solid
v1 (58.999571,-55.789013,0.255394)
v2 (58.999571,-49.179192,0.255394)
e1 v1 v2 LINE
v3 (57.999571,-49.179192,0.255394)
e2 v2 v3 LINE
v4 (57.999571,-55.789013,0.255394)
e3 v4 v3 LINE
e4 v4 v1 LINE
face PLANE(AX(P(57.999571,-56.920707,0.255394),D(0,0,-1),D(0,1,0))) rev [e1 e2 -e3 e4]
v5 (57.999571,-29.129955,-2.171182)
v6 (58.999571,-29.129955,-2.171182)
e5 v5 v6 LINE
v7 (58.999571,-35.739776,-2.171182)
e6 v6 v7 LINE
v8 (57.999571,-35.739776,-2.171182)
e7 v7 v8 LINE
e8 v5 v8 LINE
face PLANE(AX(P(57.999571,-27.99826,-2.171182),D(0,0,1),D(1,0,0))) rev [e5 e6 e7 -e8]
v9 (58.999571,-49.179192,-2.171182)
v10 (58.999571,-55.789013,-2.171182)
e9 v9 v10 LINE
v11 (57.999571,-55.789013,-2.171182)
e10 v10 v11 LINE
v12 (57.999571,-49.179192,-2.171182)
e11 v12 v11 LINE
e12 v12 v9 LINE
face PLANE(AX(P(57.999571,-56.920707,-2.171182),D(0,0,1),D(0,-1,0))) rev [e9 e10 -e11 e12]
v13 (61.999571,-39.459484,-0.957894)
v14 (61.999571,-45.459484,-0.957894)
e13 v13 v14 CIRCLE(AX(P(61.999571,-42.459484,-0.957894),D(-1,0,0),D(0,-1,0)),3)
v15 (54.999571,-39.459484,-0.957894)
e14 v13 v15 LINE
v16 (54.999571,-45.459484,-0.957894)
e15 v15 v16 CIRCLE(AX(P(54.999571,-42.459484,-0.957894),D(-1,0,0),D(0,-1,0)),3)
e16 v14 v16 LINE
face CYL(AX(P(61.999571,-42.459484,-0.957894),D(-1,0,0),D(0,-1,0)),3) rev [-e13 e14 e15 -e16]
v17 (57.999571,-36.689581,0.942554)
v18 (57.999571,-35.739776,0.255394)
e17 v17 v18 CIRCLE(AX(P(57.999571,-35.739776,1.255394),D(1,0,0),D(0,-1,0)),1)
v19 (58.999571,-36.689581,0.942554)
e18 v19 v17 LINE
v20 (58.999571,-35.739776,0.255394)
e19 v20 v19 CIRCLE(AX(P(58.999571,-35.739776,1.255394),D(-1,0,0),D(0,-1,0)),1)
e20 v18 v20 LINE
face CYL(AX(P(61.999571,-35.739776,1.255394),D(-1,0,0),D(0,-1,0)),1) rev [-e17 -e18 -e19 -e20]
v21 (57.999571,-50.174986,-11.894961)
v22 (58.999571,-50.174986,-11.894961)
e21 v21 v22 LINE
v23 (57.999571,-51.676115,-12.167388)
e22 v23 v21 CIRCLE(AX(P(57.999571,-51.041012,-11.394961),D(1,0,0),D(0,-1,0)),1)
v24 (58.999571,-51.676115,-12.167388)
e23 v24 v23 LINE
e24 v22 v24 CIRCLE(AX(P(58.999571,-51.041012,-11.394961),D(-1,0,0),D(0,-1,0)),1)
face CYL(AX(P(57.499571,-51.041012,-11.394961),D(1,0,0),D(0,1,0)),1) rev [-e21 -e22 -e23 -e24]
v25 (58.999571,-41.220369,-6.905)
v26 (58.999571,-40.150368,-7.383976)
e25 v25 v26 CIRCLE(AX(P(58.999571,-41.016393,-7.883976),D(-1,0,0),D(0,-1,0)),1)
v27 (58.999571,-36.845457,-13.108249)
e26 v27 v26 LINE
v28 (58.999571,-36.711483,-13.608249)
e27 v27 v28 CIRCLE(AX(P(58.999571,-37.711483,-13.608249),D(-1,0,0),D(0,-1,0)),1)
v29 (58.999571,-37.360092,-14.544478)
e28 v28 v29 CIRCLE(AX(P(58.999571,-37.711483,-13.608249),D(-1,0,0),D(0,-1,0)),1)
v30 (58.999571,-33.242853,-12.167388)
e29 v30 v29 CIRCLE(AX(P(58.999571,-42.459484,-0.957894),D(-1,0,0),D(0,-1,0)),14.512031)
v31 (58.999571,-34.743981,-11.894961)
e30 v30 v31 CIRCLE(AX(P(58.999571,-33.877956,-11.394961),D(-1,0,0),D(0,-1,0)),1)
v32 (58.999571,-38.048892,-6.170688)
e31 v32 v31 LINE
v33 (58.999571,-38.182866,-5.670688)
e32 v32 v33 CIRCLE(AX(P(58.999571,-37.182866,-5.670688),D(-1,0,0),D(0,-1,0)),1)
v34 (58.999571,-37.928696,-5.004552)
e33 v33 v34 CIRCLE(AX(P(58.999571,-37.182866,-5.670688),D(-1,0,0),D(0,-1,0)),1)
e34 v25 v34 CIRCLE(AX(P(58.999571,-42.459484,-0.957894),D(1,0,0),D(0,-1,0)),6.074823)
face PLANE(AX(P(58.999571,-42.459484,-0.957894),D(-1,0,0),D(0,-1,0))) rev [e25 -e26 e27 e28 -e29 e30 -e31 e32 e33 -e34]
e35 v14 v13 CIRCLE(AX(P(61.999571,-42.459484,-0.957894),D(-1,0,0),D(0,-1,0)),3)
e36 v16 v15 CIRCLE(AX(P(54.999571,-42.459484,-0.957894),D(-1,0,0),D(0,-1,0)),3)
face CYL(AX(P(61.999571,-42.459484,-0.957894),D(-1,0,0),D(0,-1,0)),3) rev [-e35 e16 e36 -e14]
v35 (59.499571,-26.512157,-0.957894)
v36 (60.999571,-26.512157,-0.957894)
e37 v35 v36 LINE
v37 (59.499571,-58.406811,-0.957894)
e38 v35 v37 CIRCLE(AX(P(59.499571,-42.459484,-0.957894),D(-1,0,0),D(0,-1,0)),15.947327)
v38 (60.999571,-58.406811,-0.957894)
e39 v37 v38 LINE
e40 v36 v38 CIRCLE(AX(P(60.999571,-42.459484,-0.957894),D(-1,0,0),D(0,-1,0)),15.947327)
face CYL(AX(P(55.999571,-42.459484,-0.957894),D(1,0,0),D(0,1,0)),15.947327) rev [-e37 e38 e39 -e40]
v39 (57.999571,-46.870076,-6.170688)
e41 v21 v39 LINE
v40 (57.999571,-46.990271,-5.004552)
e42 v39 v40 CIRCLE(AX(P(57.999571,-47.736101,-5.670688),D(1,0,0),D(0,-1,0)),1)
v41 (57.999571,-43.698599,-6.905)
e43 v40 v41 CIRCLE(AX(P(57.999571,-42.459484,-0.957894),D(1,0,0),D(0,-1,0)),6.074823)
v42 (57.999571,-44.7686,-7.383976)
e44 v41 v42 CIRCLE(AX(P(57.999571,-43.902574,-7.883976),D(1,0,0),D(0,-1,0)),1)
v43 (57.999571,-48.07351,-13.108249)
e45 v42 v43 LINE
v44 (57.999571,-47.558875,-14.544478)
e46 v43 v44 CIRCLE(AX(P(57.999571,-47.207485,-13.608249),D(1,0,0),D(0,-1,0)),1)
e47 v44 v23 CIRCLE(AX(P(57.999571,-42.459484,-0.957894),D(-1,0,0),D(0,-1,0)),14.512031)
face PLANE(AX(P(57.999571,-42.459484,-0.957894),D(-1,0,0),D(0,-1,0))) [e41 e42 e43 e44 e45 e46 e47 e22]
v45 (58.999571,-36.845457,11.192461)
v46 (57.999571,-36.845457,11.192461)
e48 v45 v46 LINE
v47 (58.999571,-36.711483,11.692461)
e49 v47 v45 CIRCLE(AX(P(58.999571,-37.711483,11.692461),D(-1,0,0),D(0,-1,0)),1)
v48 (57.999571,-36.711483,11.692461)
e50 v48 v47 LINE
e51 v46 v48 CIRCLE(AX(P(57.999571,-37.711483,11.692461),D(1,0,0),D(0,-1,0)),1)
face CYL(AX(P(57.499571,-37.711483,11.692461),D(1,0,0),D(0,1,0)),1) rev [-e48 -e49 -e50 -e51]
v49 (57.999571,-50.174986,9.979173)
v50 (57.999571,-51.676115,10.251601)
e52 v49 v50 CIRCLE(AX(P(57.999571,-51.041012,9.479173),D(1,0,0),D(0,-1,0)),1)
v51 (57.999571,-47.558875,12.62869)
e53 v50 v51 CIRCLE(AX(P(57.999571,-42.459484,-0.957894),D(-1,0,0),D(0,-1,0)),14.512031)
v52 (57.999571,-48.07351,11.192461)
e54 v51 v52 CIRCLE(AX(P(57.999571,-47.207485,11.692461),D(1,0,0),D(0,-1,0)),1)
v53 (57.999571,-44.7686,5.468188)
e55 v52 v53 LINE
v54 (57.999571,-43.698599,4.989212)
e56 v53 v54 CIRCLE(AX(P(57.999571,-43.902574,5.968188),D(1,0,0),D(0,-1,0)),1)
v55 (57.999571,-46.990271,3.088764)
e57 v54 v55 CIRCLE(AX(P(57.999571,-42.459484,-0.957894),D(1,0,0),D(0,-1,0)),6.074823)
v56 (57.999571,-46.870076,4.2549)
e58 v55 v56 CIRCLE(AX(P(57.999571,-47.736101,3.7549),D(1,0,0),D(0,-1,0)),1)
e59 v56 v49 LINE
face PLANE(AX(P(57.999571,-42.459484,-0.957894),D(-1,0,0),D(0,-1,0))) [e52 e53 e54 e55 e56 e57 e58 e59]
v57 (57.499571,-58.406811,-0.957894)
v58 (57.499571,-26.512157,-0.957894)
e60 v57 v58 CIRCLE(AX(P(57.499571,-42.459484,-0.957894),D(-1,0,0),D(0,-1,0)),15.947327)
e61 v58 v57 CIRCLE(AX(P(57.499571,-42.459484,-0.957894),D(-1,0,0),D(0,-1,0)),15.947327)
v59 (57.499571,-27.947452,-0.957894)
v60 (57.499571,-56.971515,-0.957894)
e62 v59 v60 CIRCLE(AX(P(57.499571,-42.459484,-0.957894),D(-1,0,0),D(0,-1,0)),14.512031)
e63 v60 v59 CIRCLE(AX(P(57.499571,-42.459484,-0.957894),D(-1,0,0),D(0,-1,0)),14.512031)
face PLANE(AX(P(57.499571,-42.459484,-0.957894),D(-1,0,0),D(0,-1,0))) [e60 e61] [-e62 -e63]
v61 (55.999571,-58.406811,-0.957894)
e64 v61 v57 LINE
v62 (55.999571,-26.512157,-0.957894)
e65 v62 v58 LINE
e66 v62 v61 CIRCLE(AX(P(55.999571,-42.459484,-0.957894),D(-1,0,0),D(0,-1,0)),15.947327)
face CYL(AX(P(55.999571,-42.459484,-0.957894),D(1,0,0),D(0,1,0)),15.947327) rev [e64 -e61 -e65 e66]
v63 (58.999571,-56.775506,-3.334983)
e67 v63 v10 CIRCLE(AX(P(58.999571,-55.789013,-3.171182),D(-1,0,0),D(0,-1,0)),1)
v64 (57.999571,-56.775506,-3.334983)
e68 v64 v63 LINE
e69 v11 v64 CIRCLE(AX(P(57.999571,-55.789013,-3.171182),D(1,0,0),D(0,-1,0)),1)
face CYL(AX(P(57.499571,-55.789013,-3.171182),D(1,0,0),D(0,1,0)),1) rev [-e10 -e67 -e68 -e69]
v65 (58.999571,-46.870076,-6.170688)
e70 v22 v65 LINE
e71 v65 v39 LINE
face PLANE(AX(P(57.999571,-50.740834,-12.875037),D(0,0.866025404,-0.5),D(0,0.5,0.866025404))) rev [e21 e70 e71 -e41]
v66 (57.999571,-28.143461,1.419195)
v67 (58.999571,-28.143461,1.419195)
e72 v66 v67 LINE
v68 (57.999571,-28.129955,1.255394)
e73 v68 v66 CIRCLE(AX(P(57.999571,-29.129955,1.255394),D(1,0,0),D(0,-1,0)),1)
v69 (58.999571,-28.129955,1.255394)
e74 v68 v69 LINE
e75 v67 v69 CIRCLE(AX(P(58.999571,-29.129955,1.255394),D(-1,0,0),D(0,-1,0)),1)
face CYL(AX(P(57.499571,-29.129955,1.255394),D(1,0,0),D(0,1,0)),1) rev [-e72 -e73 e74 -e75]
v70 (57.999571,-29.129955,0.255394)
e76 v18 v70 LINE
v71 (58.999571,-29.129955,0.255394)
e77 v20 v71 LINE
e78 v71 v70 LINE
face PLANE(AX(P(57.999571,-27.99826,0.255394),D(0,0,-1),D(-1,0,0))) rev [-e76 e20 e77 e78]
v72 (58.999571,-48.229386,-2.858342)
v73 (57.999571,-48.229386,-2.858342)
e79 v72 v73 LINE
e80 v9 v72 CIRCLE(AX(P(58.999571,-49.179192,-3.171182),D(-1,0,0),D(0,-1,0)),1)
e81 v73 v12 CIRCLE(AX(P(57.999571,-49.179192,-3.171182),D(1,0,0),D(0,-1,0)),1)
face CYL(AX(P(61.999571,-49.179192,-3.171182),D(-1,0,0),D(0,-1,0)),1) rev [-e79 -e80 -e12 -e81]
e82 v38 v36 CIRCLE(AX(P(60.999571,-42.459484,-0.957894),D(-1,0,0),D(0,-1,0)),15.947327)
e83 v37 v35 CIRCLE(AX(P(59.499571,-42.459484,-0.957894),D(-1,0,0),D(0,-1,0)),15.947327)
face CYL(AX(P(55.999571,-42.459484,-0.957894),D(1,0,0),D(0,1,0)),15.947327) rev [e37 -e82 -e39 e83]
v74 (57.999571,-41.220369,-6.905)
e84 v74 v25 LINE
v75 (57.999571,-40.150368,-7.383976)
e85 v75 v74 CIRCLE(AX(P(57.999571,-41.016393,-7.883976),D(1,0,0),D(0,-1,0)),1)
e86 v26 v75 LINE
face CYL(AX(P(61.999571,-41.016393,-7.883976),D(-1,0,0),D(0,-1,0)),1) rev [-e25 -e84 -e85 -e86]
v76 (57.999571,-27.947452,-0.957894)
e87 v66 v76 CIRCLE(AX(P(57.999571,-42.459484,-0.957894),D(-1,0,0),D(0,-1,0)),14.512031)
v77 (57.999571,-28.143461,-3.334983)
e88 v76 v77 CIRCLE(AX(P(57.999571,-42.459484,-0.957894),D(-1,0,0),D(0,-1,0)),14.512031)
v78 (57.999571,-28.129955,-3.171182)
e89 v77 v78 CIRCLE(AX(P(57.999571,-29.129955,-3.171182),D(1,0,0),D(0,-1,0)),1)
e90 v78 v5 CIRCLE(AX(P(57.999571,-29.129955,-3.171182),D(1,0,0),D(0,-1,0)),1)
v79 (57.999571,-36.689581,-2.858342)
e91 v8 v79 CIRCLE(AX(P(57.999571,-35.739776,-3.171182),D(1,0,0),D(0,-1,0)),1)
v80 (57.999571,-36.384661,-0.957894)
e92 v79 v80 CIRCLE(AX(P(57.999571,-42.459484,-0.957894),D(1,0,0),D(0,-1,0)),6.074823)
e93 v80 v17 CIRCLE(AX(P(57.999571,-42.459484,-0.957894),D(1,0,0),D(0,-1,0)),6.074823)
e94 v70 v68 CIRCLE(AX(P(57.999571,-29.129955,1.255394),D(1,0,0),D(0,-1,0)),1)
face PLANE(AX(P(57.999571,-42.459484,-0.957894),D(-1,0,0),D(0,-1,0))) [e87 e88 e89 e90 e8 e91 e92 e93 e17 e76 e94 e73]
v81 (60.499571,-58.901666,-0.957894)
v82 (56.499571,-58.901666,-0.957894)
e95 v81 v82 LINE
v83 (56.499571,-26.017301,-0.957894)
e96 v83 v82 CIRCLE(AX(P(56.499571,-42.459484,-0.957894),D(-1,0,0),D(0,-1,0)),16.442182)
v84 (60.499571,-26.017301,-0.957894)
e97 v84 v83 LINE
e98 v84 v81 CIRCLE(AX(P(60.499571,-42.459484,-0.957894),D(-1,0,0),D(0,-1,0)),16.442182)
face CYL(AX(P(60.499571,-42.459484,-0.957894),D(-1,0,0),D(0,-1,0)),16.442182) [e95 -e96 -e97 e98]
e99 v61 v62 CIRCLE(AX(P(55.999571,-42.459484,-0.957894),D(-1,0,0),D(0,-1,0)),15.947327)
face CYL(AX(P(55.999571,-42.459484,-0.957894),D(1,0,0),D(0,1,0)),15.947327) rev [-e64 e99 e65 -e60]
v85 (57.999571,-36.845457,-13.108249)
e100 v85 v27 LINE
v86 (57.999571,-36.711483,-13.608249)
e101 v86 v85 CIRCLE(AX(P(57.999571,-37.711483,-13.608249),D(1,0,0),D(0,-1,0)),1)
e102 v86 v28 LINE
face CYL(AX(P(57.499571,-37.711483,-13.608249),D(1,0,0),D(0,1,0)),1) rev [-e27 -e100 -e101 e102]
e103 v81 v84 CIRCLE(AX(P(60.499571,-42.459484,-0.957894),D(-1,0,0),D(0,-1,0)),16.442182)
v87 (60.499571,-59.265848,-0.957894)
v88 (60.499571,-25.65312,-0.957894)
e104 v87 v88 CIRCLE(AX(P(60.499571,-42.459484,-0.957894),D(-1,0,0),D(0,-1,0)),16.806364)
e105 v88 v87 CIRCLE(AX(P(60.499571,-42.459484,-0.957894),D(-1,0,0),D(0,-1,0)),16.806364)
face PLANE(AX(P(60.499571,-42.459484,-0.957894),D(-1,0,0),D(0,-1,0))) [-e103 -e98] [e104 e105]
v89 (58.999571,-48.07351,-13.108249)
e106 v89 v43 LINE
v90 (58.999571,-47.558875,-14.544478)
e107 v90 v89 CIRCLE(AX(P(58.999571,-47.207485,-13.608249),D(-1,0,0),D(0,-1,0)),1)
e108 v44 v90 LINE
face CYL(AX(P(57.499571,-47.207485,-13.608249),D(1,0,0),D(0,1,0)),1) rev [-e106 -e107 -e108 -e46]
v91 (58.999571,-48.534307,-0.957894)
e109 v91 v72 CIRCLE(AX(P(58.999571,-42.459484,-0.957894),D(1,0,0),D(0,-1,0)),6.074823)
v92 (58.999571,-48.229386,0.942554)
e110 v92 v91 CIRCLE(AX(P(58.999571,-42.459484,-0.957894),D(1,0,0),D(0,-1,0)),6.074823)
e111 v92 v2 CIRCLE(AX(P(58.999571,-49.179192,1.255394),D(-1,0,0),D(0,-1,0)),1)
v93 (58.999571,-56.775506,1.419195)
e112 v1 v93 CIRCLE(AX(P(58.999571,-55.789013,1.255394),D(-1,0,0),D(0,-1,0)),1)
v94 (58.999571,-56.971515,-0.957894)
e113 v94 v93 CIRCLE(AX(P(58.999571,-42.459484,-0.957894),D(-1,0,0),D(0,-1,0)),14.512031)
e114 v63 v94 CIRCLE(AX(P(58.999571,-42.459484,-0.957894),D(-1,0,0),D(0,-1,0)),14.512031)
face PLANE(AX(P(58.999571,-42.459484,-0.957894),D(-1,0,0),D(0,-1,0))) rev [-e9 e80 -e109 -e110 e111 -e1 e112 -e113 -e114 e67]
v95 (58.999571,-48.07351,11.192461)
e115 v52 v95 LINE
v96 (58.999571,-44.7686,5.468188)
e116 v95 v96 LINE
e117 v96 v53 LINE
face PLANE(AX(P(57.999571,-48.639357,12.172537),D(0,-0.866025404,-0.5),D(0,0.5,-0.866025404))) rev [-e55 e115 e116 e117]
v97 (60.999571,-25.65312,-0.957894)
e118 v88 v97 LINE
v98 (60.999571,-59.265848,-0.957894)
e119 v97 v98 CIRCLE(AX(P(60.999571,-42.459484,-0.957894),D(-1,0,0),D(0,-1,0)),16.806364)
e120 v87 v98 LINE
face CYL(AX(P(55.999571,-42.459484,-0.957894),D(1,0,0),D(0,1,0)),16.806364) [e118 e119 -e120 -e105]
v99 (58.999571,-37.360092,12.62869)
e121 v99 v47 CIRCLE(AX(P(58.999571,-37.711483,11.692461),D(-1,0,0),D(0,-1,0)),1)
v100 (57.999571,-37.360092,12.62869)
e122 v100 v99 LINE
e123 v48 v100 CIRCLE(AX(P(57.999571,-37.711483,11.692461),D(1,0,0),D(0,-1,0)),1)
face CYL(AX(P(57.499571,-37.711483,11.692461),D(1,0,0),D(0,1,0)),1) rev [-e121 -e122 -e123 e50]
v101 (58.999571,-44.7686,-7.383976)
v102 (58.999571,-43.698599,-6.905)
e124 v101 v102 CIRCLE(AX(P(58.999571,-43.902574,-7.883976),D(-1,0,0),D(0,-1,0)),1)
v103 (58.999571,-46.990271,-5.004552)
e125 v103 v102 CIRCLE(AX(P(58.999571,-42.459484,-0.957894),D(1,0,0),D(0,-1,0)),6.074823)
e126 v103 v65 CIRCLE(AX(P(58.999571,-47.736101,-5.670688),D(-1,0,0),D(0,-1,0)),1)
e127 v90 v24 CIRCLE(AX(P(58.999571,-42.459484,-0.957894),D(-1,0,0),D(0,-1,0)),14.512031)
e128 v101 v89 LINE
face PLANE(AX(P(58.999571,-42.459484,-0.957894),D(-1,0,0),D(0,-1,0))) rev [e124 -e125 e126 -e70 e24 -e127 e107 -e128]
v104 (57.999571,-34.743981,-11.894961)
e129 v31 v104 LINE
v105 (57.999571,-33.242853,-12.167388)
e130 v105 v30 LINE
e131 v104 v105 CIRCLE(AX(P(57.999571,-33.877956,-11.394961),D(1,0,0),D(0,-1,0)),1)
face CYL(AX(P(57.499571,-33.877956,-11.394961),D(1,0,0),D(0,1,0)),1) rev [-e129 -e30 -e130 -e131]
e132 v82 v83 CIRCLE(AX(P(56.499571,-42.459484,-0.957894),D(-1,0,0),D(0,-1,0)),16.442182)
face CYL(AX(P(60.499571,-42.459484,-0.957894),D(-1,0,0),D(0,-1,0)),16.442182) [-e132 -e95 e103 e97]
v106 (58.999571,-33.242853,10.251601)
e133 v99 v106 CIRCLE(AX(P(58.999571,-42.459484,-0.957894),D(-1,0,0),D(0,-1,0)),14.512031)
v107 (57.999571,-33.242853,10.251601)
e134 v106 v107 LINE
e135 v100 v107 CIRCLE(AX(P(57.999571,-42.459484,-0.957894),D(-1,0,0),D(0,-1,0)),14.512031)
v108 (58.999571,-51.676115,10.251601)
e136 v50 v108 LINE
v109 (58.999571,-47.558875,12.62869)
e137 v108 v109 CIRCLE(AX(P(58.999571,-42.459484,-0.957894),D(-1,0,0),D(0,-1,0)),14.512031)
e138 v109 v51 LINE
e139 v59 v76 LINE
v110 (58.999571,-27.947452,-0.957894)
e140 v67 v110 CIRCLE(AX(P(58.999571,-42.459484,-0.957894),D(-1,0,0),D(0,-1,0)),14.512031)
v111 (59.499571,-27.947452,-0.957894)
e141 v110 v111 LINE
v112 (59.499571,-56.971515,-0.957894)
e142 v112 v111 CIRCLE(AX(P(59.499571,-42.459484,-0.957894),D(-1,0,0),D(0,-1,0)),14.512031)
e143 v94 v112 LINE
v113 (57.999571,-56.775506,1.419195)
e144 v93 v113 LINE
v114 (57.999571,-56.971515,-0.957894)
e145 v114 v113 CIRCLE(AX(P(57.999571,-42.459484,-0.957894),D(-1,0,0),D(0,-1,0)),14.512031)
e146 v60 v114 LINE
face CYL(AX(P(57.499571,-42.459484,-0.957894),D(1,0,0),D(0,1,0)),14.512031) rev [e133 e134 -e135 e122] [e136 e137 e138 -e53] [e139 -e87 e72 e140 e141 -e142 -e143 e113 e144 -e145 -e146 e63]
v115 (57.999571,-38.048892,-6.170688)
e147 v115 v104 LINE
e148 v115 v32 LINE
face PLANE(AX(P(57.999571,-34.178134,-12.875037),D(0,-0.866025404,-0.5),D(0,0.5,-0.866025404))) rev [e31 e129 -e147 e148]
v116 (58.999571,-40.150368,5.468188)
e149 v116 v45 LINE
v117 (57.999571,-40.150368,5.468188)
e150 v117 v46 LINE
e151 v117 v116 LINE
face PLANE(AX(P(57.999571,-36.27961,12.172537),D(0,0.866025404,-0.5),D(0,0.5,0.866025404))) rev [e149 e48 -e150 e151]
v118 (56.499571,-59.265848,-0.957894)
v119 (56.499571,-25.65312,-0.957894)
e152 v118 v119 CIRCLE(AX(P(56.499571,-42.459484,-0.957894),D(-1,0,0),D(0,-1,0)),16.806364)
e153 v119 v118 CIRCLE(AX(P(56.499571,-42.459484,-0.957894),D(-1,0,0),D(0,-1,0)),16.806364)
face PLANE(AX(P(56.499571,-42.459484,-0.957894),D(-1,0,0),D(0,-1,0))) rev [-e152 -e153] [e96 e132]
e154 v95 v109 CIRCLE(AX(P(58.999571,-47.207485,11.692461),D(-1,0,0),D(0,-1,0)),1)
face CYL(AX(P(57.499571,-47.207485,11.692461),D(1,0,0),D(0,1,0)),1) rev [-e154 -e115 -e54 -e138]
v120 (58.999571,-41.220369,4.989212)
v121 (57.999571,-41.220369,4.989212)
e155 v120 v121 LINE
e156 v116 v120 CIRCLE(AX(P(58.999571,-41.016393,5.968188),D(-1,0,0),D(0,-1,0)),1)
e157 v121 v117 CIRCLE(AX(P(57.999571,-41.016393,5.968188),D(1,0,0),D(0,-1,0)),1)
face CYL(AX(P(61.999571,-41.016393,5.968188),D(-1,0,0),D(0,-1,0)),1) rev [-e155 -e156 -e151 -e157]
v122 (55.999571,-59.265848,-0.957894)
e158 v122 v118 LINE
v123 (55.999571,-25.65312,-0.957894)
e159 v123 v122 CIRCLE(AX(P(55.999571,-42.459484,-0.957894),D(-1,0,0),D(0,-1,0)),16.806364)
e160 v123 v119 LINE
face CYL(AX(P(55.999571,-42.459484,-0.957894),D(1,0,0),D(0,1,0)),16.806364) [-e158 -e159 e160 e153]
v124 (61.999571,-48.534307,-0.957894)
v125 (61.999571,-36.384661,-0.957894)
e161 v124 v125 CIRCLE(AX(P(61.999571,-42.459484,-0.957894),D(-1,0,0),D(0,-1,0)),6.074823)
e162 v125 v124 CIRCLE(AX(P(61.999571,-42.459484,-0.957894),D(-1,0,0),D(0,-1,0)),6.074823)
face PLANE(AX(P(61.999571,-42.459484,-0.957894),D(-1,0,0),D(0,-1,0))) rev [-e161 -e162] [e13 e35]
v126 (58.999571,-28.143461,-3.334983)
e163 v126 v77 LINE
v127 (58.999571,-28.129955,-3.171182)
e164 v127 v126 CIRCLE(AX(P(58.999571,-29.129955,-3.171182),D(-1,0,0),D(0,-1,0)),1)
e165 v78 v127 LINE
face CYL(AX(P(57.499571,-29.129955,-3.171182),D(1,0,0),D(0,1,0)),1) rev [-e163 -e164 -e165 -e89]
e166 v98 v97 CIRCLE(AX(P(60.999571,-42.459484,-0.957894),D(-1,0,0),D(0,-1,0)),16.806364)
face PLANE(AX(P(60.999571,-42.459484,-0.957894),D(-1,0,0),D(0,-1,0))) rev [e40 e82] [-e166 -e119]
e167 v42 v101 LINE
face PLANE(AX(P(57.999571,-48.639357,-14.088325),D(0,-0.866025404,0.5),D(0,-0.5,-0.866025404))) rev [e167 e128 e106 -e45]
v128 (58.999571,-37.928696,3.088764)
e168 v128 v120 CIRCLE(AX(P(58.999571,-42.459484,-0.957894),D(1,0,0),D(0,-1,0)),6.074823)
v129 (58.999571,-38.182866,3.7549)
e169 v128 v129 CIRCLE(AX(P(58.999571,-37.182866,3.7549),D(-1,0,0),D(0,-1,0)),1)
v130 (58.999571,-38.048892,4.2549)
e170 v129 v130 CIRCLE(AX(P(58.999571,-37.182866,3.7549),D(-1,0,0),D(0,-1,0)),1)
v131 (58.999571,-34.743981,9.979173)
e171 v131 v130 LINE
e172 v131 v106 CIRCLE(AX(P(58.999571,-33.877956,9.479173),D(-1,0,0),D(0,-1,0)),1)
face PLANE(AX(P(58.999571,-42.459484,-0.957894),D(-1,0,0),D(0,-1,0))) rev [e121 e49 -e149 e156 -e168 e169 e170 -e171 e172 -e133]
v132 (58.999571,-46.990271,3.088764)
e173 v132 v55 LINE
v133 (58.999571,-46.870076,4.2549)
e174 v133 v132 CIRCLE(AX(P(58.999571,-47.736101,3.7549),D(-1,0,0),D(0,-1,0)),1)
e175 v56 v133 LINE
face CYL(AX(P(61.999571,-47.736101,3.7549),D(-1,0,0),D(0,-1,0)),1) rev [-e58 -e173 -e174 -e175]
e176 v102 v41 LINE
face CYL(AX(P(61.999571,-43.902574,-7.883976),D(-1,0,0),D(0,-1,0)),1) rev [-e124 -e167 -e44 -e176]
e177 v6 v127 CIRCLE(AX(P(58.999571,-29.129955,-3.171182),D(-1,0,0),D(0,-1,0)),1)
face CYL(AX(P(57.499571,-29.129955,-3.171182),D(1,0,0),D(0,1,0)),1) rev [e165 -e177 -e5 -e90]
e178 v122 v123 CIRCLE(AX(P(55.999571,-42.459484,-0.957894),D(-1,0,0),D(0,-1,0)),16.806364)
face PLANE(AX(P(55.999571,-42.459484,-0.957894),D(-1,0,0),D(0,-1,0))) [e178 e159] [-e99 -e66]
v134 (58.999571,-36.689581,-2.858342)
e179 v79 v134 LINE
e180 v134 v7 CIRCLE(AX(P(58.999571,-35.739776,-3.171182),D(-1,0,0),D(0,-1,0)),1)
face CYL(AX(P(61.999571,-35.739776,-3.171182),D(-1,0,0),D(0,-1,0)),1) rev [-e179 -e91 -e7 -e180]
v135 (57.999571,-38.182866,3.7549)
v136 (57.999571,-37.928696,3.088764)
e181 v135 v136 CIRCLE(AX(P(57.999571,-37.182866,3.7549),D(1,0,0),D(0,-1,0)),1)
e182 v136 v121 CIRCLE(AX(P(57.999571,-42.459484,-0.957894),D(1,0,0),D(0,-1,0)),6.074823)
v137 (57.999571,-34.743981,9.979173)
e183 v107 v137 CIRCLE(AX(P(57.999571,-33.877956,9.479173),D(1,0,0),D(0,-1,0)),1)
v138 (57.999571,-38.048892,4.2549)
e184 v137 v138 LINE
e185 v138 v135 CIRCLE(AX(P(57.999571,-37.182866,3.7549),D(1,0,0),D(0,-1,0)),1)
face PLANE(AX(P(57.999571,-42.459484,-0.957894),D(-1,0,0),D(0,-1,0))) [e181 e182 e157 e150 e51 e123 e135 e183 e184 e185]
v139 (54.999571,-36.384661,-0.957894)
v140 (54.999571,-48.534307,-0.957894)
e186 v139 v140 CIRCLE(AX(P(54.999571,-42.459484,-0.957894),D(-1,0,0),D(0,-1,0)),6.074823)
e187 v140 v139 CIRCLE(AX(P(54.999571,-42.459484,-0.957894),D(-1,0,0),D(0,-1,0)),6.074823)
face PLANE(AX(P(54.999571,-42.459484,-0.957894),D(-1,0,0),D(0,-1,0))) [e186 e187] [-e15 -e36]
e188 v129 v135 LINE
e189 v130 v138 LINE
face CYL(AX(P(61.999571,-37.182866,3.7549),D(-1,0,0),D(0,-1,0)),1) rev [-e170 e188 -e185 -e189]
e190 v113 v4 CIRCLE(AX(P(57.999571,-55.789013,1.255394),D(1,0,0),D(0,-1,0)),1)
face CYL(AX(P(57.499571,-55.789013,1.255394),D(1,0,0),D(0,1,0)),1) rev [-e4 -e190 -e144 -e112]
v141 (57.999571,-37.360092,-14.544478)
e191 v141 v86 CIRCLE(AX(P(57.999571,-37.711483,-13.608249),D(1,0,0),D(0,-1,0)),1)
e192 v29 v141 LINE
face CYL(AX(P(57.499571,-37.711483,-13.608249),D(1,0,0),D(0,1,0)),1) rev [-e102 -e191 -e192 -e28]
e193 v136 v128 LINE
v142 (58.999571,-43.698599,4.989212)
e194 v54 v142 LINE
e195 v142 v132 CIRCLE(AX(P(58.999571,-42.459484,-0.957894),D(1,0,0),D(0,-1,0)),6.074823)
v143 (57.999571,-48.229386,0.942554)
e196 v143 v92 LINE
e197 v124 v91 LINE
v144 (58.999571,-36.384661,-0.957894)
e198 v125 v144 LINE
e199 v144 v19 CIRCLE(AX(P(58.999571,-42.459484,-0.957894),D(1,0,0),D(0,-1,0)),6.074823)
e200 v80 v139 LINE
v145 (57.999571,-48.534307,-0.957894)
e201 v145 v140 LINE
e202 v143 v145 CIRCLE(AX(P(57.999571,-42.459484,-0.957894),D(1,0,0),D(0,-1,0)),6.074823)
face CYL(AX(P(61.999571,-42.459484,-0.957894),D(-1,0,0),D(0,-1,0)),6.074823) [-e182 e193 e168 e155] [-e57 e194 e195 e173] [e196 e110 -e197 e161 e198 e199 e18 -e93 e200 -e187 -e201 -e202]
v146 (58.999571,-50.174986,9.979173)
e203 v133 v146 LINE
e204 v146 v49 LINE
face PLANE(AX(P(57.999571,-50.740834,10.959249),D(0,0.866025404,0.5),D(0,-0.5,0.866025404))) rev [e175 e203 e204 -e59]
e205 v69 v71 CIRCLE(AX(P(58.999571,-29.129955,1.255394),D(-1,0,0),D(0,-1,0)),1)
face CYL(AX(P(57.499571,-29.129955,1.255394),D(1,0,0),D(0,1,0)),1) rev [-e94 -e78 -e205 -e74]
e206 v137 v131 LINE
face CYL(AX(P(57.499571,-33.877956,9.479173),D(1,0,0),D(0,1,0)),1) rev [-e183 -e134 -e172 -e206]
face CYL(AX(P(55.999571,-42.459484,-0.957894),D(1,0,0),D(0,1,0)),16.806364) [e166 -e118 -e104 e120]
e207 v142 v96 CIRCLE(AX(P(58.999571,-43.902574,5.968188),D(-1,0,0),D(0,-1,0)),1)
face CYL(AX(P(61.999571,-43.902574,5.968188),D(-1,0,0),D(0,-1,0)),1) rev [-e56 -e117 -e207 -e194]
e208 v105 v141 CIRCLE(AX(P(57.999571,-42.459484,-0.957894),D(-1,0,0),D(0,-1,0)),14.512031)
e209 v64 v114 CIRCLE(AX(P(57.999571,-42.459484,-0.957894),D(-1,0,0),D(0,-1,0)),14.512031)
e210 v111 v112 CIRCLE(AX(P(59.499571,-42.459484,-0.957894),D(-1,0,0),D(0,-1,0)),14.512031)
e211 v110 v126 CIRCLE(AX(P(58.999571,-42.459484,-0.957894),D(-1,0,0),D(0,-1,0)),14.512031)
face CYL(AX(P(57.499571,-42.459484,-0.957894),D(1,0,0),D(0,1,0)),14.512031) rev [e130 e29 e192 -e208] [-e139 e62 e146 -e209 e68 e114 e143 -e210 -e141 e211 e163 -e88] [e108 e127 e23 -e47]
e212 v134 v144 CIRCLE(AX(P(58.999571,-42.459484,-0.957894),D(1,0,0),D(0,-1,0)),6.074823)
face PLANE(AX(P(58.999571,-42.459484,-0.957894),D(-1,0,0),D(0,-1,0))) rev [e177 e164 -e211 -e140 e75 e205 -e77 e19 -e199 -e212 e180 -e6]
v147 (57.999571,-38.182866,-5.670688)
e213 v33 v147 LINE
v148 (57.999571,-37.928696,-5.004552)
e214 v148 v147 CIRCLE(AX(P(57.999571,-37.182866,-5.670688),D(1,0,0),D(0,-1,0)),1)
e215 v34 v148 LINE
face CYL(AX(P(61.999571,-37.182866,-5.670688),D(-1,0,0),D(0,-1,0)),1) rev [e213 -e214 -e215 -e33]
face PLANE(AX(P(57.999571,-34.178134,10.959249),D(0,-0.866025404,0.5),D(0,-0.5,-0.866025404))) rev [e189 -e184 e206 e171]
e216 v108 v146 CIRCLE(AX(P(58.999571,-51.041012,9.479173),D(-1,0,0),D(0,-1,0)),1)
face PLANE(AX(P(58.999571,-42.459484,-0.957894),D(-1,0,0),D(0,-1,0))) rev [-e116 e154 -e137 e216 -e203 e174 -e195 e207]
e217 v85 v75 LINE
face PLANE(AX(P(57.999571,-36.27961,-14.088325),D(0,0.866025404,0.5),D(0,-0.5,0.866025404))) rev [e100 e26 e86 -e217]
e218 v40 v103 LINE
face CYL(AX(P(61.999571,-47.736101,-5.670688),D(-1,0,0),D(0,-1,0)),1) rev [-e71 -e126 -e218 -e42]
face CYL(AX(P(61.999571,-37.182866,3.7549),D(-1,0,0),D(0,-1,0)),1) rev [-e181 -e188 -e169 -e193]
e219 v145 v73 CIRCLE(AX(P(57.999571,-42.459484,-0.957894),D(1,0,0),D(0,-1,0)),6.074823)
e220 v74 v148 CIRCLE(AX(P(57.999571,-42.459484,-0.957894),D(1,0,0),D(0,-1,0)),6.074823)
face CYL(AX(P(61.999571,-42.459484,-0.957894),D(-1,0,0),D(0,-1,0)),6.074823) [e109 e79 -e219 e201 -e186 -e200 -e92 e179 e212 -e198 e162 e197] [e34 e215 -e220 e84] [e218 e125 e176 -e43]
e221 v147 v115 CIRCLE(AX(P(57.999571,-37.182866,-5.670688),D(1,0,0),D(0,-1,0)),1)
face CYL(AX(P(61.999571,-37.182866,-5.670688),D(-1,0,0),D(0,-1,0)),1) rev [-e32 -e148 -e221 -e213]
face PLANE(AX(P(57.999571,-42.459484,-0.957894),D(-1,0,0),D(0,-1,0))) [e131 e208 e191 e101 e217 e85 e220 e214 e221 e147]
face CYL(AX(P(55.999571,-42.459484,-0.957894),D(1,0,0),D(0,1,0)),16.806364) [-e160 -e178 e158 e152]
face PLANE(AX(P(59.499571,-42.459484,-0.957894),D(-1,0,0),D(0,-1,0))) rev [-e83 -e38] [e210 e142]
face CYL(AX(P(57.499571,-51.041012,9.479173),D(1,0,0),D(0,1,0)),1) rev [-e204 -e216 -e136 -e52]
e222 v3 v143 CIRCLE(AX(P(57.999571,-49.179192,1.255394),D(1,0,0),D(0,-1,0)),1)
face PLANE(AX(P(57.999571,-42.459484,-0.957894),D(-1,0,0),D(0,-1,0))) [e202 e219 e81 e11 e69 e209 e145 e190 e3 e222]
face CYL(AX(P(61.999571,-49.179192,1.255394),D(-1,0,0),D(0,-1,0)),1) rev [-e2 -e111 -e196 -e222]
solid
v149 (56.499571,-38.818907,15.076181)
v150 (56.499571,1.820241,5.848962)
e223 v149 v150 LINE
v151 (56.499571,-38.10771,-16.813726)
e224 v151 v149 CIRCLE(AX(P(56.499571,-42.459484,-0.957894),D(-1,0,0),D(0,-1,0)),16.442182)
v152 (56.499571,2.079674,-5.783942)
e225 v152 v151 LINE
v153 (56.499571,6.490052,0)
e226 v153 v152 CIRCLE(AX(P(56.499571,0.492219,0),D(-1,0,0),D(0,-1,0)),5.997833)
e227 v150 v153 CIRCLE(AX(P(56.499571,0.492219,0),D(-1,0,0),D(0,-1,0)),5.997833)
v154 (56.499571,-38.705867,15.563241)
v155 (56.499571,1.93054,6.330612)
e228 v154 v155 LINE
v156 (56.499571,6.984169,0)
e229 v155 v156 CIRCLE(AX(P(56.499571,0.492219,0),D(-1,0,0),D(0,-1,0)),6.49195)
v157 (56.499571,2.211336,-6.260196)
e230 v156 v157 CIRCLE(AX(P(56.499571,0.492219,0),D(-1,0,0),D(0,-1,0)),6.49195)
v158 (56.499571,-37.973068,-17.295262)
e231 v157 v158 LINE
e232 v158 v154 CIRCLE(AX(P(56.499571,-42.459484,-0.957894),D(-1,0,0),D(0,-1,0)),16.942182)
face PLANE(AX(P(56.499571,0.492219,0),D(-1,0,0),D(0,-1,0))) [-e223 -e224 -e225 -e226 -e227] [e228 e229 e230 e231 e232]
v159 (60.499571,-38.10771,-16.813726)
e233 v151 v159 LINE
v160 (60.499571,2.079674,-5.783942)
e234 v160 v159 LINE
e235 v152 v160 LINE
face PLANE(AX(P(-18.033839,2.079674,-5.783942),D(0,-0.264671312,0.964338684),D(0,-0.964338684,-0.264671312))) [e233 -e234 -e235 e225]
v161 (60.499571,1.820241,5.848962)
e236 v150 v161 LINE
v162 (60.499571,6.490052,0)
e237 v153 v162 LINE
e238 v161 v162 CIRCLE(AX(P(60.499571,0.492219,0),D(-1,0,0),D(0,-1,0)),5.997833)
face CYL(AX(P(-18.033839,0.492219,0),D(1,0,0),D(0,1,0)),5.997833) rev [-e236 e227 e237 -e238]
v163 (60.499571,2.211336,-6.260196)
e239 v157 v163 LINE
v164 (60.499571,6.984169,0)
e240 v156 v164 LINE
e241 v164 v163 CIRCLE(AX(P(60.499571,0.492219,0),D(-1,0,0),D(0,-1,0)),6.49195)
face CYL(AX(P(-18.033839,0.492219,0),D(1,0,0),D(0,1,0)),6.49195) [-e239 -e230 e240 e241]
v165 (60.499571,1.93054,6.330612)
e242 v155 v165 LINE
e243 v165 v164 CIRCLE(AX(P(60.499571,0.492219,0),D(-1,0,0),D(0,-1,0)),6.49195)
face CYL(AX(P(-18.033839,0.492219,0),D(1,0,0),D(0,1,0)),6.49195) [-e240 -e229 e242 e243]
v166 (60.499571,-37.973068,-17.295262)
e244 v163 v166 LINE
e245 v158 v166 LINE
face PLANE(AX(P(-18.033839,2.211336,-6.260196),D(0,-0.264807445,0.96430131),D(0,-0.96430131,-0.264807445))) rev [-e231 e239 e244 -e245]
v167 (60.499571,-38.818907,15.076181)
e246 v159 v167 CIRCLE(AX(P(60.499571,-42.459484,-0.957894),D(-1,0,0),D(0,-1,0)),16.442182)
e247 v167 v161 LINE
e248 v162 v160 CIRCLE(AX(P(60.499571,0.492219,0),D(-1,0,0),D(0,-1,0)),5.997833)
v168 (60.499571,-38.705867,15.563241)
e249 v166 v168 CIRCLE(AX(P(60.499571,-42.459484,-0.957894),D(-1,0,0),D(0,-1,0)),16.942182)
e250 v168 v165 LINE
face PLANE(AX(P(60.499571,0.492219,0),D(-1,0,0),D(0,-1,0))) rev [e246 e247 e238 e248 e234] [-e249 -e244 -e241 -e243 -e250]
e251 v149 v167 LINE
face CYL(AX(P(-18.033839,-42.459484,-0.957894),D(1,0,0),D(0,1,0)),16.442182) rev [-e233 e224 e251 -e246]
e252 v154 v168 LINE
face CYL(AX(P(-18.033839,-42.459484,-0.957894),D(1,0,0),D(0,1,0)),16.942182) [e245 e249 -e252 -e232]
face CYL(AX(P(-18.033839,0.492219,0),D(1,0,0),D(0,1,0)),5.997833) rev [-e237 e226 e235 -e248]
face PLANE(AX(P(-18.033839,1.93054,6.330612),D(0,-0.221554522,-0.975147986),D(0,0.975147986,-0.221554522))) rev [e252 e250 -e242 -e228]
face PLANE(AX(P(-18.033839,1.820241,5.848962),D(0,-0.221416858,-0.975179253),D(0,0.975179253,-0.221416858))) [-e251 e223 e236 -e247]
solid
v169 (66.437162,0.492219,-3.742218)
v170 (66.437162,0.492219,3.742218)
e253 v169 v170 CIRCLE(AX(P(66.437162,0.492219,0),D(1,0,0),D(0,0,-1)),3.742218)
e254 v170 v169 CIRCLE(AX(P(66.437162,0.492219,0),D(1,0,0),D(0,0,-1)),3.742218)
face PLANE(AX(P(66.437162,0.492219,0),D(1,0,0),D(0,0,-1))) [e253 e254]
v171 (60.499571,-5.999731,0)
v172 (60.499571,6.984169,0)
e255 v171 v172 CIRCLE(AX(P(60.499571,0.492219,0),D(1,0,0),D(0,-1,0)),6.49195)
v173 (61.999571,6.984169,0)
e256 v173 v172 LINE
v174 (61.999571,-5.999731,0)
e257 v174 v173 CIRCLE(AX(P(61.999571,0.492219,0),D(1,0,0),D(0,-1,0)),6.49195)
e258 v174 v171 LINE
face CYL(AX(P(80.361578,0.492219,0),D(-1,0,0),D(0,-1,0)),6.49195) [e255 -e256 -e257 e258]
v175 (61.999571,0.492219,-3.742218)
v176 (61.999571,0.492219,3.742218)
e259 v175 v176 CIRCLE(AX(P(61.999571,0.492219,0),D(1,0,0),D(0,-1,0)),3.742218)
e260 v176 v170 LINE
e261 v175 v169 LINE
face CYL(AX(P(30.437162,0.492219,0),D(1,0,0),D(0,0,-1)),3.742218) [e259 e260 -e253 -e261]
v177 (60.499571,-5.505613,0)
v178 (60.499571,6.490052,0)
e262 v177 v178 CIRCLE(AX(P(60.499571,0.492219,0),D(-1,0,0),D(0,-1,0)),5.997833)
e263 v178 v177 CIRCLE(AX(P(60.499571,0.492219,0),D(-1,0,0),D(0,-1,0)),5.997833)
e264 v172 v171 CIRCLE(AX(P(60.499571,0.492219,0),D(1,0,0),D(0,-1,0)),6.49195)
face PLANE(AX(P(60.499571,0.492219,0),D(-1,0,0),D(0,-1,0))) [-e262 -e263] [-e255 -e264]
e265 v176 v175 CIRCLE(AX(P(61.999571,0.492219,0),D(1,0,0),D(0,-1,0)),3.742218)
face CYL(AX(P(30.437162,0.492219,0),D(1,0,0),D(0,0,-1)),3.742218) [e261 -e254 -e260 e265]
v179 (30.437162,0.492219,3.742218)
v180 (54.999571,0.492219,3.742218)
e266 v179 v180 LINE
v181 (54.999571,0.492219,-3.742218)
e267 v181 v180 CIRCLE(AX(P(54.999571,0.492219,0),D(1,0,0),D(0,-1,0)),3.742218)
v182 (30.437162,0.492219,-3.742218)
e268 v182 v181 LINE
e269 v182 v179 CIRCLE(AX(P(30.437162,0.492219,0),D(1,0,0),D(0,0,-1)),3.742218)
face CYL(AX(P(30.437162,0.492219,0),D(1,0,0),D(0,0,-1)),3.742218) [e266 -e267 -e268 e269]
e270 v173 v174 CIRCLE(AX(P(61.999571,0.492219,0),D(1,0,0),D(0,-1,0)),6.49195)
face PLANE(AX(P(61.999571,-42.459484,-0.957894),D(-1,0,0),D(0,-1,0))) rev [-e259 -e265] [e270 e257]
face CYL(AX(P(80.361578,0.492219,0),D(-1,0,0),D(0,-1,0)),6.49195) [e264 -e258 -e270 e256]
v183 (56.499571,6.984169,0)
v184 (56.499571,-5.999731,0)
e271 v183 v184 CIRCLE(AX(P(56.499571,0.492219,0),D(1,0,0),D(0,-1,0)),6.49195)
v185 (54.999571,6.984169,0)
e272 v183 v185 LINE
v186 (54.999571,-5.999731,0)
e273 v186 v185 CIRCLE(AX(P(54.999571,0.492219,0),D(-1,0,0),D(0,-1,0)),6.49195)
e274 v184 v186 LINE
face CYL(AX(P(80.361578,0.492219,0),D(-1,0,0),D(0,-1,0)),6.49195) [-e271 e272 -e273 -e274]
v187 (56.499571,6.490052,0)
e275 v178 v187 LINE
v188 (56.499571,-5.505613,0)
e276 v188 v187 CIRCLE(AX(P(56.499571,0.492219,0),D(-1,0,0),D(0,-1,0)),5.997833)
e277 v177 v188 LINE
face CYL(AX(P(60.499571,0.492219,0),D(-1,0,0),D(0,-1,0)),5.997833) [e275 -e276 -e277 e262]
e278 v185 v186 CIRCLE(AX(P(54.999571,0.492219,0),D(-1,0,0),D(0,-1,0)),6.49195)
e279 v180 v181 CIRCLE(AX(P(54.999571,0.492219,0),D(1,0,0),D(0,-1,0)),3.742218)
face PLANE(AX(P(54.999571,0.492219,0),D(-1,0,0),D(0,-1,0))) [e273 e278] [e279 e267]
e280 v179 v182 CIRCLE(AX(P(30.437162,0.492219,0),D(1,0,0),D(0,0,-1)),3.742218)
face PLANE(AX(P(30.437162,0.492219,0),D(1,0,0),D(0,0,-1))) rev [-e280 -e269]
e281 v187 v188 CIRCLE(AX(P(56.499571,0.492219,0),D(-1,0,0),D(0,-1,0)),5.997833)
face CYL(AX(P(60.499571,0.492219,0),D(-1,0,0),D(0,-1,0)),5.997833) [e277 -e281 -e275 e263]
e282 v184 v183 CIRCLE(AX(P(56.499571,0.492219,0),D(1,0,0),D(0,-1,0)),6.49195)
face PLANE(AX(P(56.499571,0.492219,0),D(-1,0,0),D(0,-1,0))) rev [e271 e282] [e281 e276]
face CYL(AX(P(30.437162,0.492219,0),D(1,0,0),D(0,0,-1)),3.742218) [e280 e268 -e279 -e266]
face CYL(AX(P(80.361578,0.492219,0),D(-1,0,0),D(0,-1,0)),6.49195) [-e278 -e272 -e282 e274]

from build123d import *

# Parameters (mm, degrees)
SKETCH2_R                = 6.074823011
SKETCH2_R_2              = 3
BOSS_EXTRUDE1_DEPTH      = 7
SKETCH3_R                = 16.806364111
SKETCH3_R_2              = 15.947327111
BOSS_EXTRUDE2_DEPTH      = 2.5
SKETCH4_R                = 15.947327111
SKETCH4_R_2              = 14.512031262
BOSS_EXTRUDE3_DEPTH      = 1
BOSS_EXTRUDE4_DEPTH      = 0.5
FILLET1_R                = 1
FILLET2_R                = 1
SKETCH6_R                = 19.088387017
SKETCH6_R_2              = 16.442182257
CUT_EXTRUDE1_DEPTH       = 2
BOSS_EXTRUDE5_DEPTH      = 32
BOSS_EXTRUDE5_DEPTH_BACK = 4
SKETCH7_R                = 3.742217825
SKETCH8_R                = 6.491949868
SKETCH8_R_2              = 3.742217825
BOSS_EXTRUDE6_DEPTH      = 7
SKETCH9_R                = 7.17344487
SKETCH9_R_2              = 5.997832818
CUT_EXTRUDE2_DEPTH       = 2
BOSS_EXTRUDE7_DEPTH      = 4


with BuildPart() as part:
    # Sketch2 → Boss-Extrude1 (new body)
    with BuildSketch(Plane.ZY.offset(-54.999571017)):
        with Locations(Location((-0.957893929, -42.45948374, 0), (0, 0, 270))):
            Circle(SKETCH2_R)
        with Locations(Location((-0.957893929, -42.45948374, 0), (0, 0, 270))):
            Circle(SKETCH2_R_2, mode=Mode.SUBTRACT)
    extrude(amount=-BOSS_EXTRUDE1_DEPTH)



with BuildPart() as body_2:
    # Sketch3 → Boss-Extrude2 (new, symmetric)
    with BuildSketch(Plane.ZY.offset(-58.499571017)):
        with Locations(Location((-0.957893929, -42.45948374, 0), (0, 0, 270))):
            Circle(SKETCH3_R)
        with Locations(Location((-0.957893929, -42.45948374, 0), (0, 0, 270))):
            Circle(SKETCH3_R_2, mode=Mode.SUBTRACT)
    extrude(amount=BOSS_EXTRUDE2_DEPTH, both=True)

    # Sketch4 → Boss-Extrude3 (add, symmetric)
    with BuildSketch(Plane.ZY.offset(-58.499571017)):
        with Locations(Location((-0.957893929, -42.45948374, 0), (0, 0, 270))):
            Circle(SKETCH4_R)
        with Locations(Location((-0.957893929, -42.45948374, 0), (0, 0, 270))):
            Circle(SKETCH4_R_2, mode=Mode.SUBTRACT)
    extrude(amount=BOSS_EXTRUDE3_DEPTH, both=True)


with BuildPart() as part_1:
    add(part.part)

    add(body_2.part)  # Boss-Extrude4 merges body 2
    # Sketch5 → Boss-Extrude4 (add, symmetric)
    with BuildSketch(Plane.ZY.offset(-58.499571017)):
        with BuildLine():
            Line((10.959248998, -34.178133861), (3.590416559, -38.432531254))
            ThreePointArc((3.590416559, -38.432531254), (4.303057122, -39.422072234), (4.803704468, -40.534007556))
            Line((4.803704468, -40.534007556), (12.172536907, -36.279610164))
            ThreePointArc((12.172536907, -36.279610164), (11.609893805, -35.203468109), (10.959248998, -34.178133861))
        make_face()
        with BuildLine():
            Line((-2.171181838, -27.998260285), (-2.171181838, -36.50705507))
            ThreePointArc((-2.171181838, -36.50705507), (-0.957893929, -36.384660729), (0.25539398, -36.50705507))
            Line((0.25539398, -36.50705507), (0.25539398, -27.998260285))
            ThreePointArc((0.25539398, -27.998260285), (-0.957893929, -27.947452478), (-2.171181838, -27.998260285))
        make_face()
        with BuildLine():
            Line((12.172536907, -48.639357316), (4.803704468, -44.384959923))
            ThreePointArc((4.803704468, -44.384959923), (4.303057122, -45.496895245), (3.590416559, -46.486436226))
            Line((3.590416559, -46.486436226), (10.959248998, -50.740833618))
            ThreePointArc((10.959248998, -50.740833618), (11.609893805, -49.715499371), (12.172536907, -48.639357316))
        make_face()
        with BuildLine():
            Line((0.25539398, -56.920707194), (0.25539398, -48.411912409))
            ThreePointArc((0.25539398, -48.411912409), (-0.957893929, -48.534306751), (-2.171181838, -48.411912409))
            Line((-2.171181838, -48.411912409), (-2.171181838, -56.920707194))
            ThreePointArc((-2.171181838, -56.920707194), (-0.957893929, -56.971515002), (0.25539398, -56.920707194))
        make_face()
        with BuildLine():
            Line((-12.875036856, -50.740833618), (-5.506204416, -46.486436226))
            ThreePointArc((-5.506204416, -46.486436226), (-6.21884498, -45.496895245), (-6.719492325, -44.384959923))
            Line((-6.719492325, -44.384959923), (-14.088324765, -48.639357316))
            ThreePointArc((-14.088324765, -48.639357316), (-13.525681662, -49.715499371), (-12.875036856, -50.740833618))
        make_face()
        with BuildLine():
            Line((-14.088324765, -36.279610164), (-6.719492325, -40.534007556))
            ThreePointArc((-6.719492325, -40.534007556), (-6.21884498, -39.422072234), (-5.506204416, -38.432531254))
            Line((-5.506204416, -38.432531254), (-12.875036856, -34.178133861))
            ThreePointArc((-12.875036856, -34.178133861), (-13.525681662, -35.203468109), (-14.088324765, -36.279610164))
        make_face()
    extrude(amount=BOSS_EXTRUDE4_DEPTH, both=True)

    # Fillet1
    fillet1_edges = [part_1.edges().sort_by_distance(p)[0] for p in [
        (58.499571017, -34.178133861, -12.875036856),
        (58.499571017, -36.279610164, -14.088324765),
        (58.499571017, -40.534007556, -6.719492325),
        (58.499571017, -38.432531254, -5.506204416),
    ]]
    fillet(fillet1_edges, radius=FILLET1_R)

    # Fillet2
    fillet2_edges = [part_1.edges().sort_by_distance(p)[0] for p in [
        (58.499571017, -27.998260285, 0.25539398),
        (58.499571017, -27.998260285, -2.171181838),
        (58.499571017, -36.50705507, -2.171181838),
        (58.499571017, -36.50705507, 0.25539398),
        (58.499571017, -36.279610164, 12.172536907),
        (58.499571017, -34.178133861, 10.959248998),
        (58.499571017, -38.432531254, 3.590416559),
        (58.499571017, -40.534007556, 4.803704468),
        (58.499571017, -50.740833618, 10.959248998),
        (58.499571017, -48.639357316, 12.172536907),
        (58.499571017, -44.384959923, 4.803704468),
        (58.499571017, -46.486436226, 3.590416559),
        (58.499571017, -56.920707194, -2.171181838),
        (58.499571017, -56.920707194, 0.25539398),
        (58.499571017, -48.411912409, 0.25539398),
        (58.499571017, -48.411912409, -2.171181838),
        (58.499571017, -48.639357316, -14.088324765),
        (58.499571017, -50.740833618, -12.875036856),
        (58.499571017, -46.486436226, -5.506204416),
        (58.499571017, -44.384959923, -6.719492325),
    ]]
    fillet(fillet2_edges, radius=FILLET2_R)

    # Sketch6 → Cut-Extrude1 (cut, symmetric)
    with BuildSketch(Plane.ZY.offset(-58.499571017)):
        with Locations((-0.957893929, -42.45948374)):
            Circle(SKETCH6_R)
        with Locations(Location((-0.957893929, -42.45948374, 0), (0, 0, 270))):
            Circle(SKETCH6_R_2, mode=Mode.SUBTRACT)
    extrude(amount=CUT_EXTRUDE1_DEPTH, both=True, mode=Mode.SUBTRACT)


with BuildPart() as body_2_2:
    # Sketch7 → Boss-Extrude5 (new, two sides: drawn at the far end of the back side and taken through both)
    with BuildSketch(Plane(origin=(34.437162011, 0, 0), x_dir=(0, 0, -1), z_dir=(1, 0, 0)).offset(-BOSS_EXTRUDE5_DEPTH_BACK)):
        with Locations((0, 0.49221935)):
            Circle(SKETCH7_R)
    extrude(amount=BOSS_EXTRUDE5_DEPTH + BOSS_EXTRUDE5_DEPTH_BACK)

    # Sketch8 → Boss-Extrude6 (add)
    with BuildSketch(Plane.ZY.offset(-54.999571017)):
        with Locations(Location((0, 0.49221935, 0), (0, 0, 270))):
            Circle(SKETCH8_R)
        with Locations(Location((0, 0.49221935, 0), (0, 0, 180))):
            Circle(SKETCH8_R_2, mode=Mode.SUBTRACT)
    extrude(amount=-BOSS_EXTRUDE6_DEPTH)

    # Sketch9 → Cut-Extrude2 (cut, symmetric)
    with BuildSketch(Plane.ZY.offset(-58.499571017)):
        with Locations((0, 0.49221935)):
            Circle(SKETCH9_R)
        with Locations(Location((0, 0.49221935, 0), (0, 0, 270))):
            Circle(SKETCH9_R_2, mode=Mode.SUBTRACT)
    extrude(amount=CUT_EXTRUDE2_DEPTH, both=True, mode=Mode.SUBTRACT)


with BuildPart() as body_3:
    # Sketch11 → Boss-Extrude7 (new body)
    with BuildSketch(Plane.ZY.offset(-60.499571017)):
        with BuildLine():
            Line((-6.260195764, 2.211336008), (-17.295262478, -37.973067741))
            ThreePointArc((-17.295262478, -37.973067741), (-1.335638653, -59.397454354), (15.56324097, -38.705866646))
            Line((15.56324097, -38.705866646), (6.330611836, 1.9305402))
            ThreePointArc((6.330611836, 1.9305402), (0.144745215, 6.98255539), (-6.260195764, 2.211336008))
        make_face()
        with BuildLine():
            Line((-5.783942204, 2.079673631), (-16.813726321, -38.10770979))
            ThreePointArc((-16.813726321, -38.10770979), (-1.324490599, -58.897578649), (15.076181077, -38.818907402))
            Line((15.076181077, -38.818907402), (5.848962125, 1.820240648))
            ThreePointArc((5.848962125, 1.820240648), (0.133728328, 6.488561171), (-5.783942204, 2.079673631))
        make_face(mode=Mode.SUBTRACT)
    extrude(amount=BOSS_EXTRUDE7_DEPTH)


solid = Compound([part_1.part, body_2_2.part, body_3.part])
